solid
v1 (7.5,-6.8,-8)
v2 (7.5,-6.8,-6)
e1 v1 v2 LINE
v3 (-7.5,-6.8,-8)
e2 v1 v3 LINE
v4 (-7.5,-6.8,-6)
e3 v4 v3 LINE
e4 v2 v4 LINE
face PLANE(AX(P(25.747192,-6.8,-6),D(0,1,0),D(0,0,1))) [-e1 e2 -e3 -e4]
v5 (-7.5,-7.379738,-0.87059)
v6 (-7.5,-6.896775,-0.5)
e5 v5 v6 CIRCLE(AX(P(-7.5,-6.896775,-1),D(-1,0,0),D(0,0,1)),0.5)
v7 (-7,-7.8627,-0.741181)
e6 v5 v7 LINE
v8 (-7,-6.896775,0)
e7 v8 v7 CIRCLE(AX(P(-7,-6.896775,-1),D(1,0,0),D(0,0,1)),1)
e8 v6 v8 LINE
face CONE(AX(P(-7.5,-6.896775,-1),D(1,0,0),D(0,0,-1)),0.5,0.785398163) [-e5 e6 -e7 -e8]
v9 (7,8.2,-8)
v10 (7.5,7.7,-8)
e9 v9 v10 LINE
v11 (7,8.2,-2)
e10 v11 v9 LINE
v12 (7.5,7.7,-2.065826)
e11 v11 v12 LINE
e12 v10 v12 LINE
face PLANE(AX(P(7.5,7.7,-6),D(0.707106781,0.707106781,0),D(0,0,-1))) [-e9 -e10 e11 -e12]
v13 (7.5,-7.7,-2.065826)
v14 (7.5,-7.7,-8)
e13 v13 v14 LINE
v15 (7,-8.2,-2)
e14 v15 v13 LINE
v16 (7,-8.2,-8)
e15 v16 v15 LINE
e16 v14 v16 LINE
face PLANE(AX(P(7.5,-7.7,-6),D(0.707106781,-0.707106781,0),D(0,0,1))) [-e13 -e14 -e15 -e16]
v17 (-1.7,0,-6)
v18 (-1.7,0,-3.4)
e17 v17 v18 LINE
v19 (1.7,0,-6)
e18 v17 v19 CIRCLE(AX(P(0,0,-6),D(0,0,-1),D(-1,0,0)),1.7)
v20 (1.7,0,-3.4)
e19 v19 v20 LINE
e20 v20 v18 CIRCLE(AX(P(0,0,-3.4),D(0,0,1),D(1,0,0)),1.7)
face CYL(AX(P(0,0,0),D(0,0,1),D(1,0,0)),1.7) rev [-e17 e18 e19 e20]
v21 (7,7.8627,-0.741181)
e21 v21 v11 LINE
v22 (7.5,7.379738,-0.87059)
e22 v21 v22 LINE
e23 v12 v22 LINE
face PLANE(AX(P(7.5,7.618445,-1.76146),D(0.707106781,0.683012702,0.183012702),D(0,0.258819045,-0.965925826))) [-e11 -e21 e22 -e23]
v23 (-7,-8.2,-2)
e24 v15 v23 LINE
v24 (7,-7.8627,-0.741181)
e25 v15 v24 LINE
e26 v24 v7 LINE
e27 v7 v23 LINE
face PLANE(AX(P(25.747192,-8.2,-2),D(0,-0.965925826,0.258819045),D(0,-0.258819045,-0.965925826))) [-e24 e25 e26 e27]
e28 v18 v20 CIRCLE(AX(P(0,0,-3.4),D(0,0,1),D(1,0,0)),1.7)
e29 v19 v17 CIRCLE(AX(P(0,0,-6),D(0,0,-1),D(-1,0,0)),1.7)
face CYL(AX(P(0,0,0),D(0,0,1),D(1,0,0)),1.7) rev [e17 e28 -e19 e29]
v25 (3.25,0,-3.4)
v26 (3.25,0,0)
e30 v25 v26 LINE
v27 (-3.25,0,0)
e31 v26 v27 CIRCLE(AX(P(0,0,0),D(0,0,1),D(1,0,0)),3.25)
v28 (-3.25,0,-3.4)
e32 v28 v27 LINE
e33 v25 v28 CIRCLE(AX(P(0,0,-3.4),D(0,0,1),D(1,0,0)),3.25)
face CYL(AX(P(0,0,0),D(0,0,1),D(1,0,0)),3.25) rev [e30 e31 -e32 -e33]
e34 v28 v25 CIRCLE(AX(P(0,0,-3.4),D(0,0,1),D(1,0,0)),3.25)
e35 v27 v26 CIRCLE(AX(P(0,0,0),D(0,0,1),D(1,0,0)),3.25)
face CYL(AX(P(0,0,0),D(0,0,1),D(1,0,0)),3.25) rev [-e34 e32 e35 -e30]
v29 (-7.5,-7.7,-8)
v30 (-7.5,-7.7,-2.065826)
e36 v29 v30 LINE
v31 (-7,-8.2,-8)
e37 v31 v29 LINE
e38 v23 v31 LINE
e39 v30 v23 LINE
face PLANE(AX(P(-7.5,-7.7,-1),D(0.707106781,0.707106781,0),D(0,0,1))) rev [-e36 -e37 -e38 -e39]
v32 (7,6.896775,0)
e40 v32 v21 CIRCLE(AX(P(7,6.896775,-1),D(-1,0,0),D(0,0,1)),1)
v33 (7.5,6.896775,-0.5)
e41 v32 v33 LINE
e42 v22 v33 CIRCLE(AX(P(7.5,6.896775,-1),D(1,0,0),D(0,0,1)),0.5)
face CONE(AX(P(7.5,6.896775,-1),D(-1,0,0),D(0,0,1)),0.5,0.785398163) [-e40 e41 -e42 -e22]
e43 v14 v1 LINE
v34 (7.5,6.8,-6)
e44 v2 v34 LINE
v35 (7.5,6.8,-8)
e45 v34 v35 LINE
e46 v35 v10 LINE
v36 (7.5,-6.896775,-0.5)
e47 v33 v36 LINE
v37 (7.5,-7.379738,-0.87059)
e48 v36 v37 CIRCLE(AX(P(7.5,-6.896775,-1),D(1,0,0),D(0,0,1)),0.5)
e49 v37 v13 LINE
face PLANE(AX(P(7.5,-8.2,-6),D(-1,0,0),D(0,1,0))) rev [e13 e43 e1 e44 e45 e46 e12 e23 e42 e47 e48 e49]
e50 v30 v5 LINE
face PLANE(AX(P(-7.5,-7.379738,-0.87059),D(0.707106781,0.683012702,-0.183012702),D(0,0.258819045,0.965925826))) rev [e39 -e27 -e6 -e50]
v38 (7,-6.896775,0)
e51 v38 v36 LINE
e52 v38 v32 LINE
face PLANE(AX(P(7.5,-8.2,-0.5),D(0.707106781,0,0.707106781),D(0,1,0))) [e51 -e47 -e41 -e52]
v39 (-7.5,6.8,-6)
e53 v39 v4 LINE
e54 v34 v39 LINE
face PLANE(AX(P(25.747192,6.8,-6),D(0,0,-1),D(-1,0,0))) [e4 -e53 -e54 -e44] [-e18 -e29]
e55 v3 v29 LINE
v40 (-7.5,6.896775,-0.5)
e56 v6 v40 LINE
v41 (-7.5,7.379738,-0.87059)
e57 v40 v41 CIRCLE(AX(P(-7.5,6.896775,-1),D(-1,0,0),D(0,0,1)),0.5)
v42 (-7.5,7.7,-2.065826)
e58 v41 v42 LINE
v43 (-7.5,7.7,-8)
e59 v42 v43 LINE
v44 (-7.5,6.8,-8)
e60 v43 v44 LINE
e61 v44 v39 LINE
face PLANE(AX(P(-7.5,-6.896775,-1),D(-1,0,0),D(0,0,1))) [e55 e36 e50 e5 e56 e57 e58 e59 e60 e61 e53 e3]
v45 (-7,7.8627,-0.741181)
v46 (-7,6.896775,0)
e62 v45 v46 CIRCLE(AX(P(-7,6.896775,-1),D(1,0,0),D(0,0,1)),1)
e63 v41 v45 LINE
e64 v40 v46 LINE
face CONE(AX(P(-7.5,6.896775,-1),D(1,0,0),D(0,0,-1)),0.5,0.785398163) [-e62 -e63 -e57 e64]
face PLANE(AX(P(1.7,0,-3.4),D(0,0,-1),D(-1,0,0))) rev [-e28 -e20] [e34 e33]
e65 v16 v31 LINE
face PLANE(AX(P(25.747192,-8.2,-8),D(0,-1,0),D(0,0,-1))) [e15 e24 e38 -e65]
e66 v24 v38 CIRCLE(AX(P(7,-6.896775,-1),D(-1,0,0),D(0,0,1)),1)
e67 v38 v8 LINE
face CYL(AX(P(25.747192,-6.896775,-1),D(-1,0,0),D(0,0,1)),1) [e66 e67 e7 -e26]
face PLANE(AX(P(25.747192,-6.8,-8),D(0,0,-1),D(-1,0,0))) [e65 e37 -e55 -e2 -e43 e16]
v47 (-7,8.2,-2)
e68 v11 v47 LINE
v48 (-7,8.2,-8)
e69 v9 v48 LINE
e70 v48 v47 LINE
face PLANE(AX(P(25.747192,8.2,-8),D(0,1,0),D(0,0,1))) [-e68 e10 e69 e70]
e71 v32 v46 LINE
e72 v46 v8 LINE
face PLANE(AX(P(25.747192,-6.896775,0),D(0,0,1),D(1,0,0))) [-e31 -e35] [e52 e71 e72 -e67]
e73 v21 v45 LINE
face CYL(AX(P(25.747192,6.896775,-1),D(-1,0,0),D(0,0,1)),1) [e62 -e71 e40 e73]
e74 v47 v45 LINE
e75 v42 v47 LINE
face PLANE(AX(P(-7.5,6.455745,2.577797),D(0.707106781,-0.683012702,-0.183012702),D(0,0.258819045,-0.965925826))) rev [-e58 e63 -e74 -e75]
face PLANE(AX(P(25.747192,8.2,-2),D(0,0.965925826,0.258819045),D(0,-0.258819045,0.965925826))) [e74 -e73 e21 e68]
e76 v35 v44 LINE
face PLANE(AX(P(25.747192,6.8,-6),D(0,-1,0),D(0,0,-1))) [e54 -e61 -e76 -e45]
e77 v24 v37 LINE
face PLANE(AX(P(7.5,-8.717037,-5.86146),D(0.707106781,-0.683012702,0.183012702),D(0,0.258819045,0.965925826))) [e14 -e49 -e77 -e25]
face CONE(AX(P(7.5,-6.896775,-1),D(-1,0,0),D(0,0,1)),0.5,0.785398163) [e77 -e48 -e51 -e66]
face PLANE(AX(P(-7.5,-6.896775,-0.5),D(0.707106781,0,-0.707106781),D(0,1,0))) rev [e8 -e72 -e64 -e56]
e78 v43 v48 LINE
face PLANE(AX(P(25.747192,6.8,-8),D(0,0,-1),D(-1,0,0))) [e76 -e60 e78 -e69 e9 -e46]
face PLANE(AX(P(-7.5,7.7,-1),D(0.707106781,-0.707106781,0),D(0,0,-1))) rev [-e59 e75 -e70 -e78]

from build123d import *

# Parameters (mm, degrees)
EXTRUDE_1_DEPTH              = 15
CHAMFER_1_SIZE               = 0.5
HOLE_WIZARD_M3_1_D           = 3.4
HOLE_WIZARD_M3_1_DEPTH       = 10
HOLE_WIZARD_M3_1_CBORE_D     = 6.5
HOLE_WIZARD_M3_1_CBORE_DEPTH = 3.4
HOLE_WIZARD_M3_1_TIP         = 1.021463052


with BuildPart() as part:
    # 草图2 → 凸台-拉伸1 (new body)
    with BuildSketch(Plane.ZY.offset(7.5)):
        with BuildLine():
            Line((-6, -6.8), (-8, -6.8))
            Line((-8, -6.8), (-8, -8.2))
            Line((-8, -8.2), (-2, -8.2))
            Line((-2, -8.2), (-0.741180955, -7.862700453))
            ThreePointArc((-0.741180955, -7.862700453), (-0.20664666, -7.505536056), (0, -6.896774627))
            Line((0, -6.896774627), (0, 6.896774627))
            ThreePointArc((0, 6.896774627), (-0.20664666, 7.505536056), (-0.741180955, 7.862700453))
            Line((-0.741180955, 7.862700453), (-2, 8.2))
            Line((-2, 8.2), (-8, 8.2))
            Line((-8, 8.2), (-8, 7.7))
            Line((-8, 7.7), (-8, 6.8))
            Line((-8, 6.8), (-6, 6.8))
            Line((-6, 6.8), (-6, -6.8))
        make_face()
    extrude(amount=-EXTRUDE_1_DEPTH)

    # 倒角1
    chamfer_1_edges = [part.edges().sort_by_distance(p)[0] for p in [
        (-7.5, 8.2, -5),
        (-7.5, 8.031350227, -1.370590477),
        (-7.5, 7.505536056, -0.20664666),
        (-7.5, 0, 0),
        (-7.5, -7.505536056, -0.20664666),
        (-7.5, -8.031350227, -1.370590477),
        (-7.5, -8.2, -5),
        (7.5, -8.2, -5),
        (7.5, -8.031350227, -1.370590477),
        (7.5, -7.505536056, -0.20664666),
        (7.5, 0, 0),
        (7.5, 7.505536056, -0.20664666),
        (7.5, 8.031350227, -1.370590477),
        (7.5, 8.2, -5),
    ]]
    chamfer(chamfer_1_edges, length=CHAMFER_1_SIZE)

    # M3 六角凹头螺钉的柱形沉头孔1
    with Locations(Plane.XY):
        with Locations((0, 0)):
            CounterBoreHole(HOLE_WIZARD_M3_1_D / 2, HOLE_WIZARD_M3_1_CBORE_D / 2, HOLE_WIZARD_M3_1_CBORE_DEPTH, depth=HOLE_WIZARD_M3_1_DEPTH)
            with Locations((0, 0, -(HOLE_WIZARD_M3_1_DEPTH + HOLE_WIZARD_M3_1_TIP / 2))):  # 118° drill point
                Cone(0, HOLE_WIZARD_M3_1_D / 2, HOLE_WIZARD_M3_1_TIP, mode=Mode.SUBTRACT)


solid = part.part
